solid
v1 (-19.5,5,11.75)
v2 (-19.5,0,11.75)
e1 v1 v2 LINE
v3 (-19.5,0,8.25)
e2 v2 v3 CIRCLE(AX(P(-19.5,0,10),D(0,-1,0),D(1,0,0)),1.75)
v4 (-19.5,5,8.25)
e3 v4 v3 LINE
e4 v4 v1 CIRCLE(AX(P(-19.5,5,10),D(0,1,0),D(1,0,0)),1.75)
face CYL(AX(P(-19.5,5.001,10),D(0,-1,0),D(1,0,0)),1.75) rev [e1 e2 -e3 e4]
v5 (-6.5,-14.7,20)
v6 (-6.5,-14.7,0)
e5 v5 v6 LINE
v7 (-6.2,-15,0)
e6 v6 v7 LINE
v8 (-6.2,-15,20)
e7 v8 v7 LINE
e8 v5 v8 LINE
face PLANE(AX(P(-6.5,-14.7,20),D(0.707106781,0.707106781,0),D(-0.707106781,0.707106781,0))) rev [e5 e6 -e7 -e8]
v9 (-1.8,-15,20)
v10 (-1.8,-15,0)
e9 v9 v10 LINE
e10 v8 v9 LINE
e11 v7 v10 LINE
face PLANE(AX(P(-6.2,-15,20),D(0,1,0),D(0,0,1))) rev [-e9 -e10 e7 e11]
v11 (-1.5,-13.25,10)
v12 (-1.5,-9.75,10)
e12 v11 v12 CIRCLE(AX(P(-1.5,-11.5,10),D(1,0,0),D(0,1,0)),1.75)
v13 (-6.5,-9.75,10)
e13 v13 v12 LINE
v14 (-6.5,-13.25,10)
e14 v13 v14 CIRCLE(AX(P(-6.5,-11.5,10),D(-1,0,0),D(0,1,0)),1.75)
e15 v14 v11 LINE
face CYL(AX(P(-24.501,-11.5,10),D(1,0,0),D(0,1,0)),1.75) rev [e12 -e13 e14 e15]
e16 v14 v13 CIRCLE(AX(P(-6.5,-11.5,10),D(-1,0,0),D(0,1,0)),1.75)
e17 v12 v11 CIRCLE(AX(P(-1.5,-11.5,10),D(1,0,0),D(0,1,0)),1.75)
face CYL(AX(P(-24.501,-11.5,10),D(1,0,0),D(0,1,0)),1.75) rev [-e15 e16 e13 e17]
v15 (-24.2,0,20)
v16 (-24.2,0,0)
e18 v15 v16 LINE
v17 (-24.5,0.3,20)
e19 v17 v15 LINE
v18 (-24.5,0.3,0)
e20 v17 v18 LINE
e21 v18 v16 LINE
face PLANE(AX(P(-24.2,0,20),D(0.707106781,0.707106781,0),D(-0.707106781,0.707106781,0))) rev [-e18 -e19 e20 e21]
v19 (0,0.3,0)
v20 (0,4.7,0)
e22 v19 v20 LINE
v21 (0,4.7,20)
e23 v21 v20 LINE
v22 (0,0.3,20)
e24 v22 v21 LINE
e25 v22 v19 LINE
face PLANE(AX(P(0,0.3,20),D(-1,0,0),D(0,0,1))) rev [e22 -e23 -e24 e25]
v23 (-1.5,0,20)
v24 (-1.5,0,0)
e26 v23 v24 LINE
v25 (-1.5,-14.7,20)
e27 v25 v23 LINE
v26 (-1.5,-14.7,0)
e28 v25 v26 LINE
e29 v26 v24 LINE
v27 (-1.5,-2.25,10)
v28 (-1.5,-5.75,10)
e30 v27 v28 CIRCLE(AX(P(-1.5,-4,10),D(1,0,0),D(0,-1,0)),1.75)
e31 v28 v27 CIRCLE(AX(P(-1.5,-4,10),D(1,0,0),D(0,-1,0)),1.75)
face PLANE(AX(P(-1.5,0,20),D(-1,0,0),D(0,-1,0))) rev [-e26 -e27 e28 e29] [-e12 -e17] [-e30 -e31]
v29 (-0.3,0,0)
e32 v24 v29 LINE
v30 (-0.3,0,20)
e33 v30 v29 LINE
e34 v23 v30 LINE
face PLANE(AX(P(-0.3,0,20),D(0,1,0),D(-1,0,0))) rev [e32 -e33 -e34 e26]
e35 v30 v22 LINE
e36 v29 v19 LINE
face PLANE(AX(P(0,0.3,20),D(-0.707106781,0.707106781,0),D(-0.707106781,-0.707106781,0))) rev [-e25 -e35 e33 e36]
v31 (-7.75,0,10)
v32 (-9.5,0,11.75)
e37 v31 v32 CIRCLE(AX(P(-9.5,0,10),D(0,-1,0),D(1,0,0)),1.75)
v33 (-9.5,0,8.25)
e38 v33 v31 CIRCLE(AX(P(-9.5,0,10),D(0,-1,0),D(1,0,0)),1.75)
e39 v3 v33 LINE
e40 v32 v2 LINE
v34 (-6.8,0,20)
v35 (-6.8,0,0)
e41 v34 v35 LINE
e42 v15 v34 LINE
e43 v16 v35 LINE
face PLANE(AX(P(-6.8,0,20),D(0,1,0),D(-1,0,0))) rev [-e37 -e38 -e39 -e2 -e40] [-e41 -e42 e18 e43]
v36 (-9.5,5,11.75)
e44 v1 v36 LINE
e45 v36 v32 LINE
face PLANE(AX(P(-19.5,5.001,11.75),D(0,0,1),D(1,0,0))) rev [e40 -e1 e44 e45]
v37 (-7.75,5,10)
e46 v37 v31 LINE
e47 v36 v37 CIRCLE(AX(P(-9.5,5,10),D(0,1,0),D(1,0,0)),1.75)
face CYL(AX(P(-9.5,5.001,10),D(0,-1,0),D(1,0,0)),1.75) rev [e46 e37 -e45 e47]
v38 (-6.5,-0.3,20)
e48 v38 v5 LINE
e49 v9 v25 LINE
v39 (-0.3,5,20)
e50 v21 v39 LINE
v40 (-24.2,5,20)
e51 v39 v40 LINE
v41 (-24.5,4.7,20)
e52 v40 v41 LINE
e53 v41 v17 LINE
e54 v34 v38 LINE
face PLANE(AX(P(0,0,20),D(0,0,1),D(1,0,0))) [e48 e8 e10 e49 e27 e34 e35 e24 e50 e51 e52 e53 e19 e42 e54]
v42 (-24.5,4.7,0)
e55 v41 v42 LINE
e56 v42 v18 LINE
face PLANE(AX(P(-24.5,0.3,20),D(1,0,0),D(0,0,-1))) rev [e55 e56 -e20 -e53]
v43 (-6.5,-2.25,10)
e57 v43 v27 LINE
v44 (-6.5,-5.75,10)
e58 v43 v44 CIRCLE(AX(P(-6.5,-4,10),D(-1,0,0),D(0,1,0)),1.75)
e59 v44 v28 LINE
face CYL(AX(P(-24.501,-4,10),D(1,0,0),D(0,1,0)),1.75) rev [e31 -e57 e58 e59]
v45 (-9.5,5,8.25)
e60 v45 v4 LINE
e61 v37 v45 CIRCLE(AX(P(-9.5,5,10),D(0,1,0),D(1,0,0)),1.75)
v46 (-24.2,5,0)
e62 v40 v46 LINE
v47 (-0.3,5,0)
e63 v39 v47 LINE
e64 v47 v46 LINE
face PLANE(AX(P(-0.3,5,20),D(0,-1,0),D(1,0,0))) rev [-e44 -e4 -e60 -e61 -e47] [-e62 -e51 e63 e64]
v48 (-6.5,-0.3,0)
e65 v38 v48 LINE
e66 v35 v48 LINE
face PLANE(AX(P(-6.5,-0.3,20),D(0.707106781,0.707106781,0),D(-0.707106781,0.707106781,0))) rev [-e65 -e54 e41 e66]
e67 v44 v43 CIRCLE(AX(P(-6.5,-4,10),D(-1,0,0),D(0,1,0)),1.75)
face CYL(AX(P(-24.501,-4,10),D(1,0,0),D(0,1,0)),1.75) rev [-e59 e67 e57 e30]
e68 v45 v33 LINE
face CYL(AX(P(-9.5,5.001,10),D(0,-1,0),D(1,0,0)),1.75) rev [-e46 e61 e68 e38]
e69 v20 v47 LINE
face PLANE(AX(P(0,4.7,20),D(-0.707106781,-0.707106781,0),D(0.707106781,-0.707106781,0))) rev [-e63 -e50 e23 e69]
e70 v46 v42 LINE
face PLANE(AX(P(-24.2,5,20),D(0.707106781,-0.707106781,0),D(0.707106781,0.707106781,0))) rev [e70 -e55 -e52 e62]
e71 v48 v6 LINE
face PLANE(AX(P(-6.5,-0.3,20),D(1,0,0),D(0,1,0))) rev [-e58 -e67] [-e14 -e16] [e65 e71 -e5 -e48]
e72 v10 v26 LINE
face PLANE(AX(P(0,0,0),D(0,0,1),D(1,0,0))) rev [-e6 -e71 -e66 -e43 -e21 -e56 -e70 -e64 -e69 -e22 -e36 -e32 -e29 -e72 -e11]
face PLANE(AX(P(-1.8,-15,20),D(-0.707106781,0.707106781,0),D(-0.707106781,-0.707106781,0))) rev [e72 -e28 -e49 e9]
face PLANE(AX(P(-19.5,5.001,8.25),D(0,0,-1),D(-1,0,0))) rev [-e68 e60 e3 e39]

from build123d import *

# Parameters (mm, degrees)
BOSS_EXTRUDE1_DEPTH = 20
CUT_EXTRUDE2_REACH  = 35.971
SKETCH2_R           = 1.75
CUT_EXTRUDE3_REACH  = 37.004


with BuildPart() as part:
    # Sketch1 → Boss-Extrude1 (new body)
    with BuildSketch(Plane.XY):
        Polygon((-6.8, 0), (-24.2, 0), (-24.5, 0.3), (-24.5, 4.7), (-24.2, 5), (-0.3, 5), (0, 4.7), (0, 0.3), (-0.3, 0), (-1.5, 0), (-1.5, -14.7), (-1.8, -15), (-6.2, -15), (-6.5, -14.7), (-6.5, -0.3), align=None)
    extrude(amount=BOSS_EXTRUDE1_DEPTH)

    # Sketch2 → Cut-Extrude2 (cut, up to next)
    with BuildSketch(Plane(origin=(-1.5, 0, 0), x_dir=(0, 0, -1), z_dir=(1, 0, 0)), mode=Mode.PRIVATE) as cut_extrude2_sk1:
        with Locations(Location((-10, -11.5, 0), (0, 0, 90))):
            Circle(SKETCH2_R)
    cut_extrude2_tool1 = extrude(cut_extrude2_sk1.sketch, amount=-CUT_EXTRUDE2_REACH, mode=Mode.PRIVATE) & part.part
    # Sketch2 → Cut-Extrude2 (cut, up to next)
    with BuildSketch(Plane(origin=(-1.5, 0, 0), x_dir=(0, 0, -1), z_dir=(1, 0, 0)), mode=Mode.PRIVATE) as cut_extrude2_sk2:
        with Locations(Location((-10, -4, 0), (0, 0, 90))):
            Circle(SKETCH2_R)
    cut_extrude2_tool2 = extrude(cut_extrude2_sk2.sketch, amount=-CUT_EXTRUDE2_REACH, mode=Mode.PRIVATE) & part.part
    add(cut_extrude2_tool1.solids().sort_by_distance((-1.5, -11.5, 10))[0], mode=Mode.SUBTRACT)
    add(cut_extrude2_tool2.solids().sort_by_distance((-1.5, -4, 10))[0], mode=Mode.SUBTRACT)

    # Sketch5 → Cut-Extrude3 (cut, up to next)
    with BuildSketch(Plane.XZ, mode=Mode.PRIVATE) as cut_extrude3_sk1:
        with BuildLine():
            Line((-19.5, 11.75), (-9.5, 11.75))
            ThreePointArc((-9.5, 11.75), (-7.75, 10), (-9.5, 8.25))
            Line((-9.5, 8.25), (-19.5, 8.25))
            ThreePointArc((-19.5, 8.25), (-21.25, 10), (-19.5, 11.75))
        make_face()
    cut_extrude3_tool1 = extrude(cut_extrude3_sk1.sketch, amount=-CUT_EXTRUDE3_REACH, mode=Mode.PRIVATE) & part.part
    add(cut_extrude3_tool1.solids().sort_by_distance((-14.5, 0, 10))[0], mode=Mode.SUBTRACT)


solid = part.part
